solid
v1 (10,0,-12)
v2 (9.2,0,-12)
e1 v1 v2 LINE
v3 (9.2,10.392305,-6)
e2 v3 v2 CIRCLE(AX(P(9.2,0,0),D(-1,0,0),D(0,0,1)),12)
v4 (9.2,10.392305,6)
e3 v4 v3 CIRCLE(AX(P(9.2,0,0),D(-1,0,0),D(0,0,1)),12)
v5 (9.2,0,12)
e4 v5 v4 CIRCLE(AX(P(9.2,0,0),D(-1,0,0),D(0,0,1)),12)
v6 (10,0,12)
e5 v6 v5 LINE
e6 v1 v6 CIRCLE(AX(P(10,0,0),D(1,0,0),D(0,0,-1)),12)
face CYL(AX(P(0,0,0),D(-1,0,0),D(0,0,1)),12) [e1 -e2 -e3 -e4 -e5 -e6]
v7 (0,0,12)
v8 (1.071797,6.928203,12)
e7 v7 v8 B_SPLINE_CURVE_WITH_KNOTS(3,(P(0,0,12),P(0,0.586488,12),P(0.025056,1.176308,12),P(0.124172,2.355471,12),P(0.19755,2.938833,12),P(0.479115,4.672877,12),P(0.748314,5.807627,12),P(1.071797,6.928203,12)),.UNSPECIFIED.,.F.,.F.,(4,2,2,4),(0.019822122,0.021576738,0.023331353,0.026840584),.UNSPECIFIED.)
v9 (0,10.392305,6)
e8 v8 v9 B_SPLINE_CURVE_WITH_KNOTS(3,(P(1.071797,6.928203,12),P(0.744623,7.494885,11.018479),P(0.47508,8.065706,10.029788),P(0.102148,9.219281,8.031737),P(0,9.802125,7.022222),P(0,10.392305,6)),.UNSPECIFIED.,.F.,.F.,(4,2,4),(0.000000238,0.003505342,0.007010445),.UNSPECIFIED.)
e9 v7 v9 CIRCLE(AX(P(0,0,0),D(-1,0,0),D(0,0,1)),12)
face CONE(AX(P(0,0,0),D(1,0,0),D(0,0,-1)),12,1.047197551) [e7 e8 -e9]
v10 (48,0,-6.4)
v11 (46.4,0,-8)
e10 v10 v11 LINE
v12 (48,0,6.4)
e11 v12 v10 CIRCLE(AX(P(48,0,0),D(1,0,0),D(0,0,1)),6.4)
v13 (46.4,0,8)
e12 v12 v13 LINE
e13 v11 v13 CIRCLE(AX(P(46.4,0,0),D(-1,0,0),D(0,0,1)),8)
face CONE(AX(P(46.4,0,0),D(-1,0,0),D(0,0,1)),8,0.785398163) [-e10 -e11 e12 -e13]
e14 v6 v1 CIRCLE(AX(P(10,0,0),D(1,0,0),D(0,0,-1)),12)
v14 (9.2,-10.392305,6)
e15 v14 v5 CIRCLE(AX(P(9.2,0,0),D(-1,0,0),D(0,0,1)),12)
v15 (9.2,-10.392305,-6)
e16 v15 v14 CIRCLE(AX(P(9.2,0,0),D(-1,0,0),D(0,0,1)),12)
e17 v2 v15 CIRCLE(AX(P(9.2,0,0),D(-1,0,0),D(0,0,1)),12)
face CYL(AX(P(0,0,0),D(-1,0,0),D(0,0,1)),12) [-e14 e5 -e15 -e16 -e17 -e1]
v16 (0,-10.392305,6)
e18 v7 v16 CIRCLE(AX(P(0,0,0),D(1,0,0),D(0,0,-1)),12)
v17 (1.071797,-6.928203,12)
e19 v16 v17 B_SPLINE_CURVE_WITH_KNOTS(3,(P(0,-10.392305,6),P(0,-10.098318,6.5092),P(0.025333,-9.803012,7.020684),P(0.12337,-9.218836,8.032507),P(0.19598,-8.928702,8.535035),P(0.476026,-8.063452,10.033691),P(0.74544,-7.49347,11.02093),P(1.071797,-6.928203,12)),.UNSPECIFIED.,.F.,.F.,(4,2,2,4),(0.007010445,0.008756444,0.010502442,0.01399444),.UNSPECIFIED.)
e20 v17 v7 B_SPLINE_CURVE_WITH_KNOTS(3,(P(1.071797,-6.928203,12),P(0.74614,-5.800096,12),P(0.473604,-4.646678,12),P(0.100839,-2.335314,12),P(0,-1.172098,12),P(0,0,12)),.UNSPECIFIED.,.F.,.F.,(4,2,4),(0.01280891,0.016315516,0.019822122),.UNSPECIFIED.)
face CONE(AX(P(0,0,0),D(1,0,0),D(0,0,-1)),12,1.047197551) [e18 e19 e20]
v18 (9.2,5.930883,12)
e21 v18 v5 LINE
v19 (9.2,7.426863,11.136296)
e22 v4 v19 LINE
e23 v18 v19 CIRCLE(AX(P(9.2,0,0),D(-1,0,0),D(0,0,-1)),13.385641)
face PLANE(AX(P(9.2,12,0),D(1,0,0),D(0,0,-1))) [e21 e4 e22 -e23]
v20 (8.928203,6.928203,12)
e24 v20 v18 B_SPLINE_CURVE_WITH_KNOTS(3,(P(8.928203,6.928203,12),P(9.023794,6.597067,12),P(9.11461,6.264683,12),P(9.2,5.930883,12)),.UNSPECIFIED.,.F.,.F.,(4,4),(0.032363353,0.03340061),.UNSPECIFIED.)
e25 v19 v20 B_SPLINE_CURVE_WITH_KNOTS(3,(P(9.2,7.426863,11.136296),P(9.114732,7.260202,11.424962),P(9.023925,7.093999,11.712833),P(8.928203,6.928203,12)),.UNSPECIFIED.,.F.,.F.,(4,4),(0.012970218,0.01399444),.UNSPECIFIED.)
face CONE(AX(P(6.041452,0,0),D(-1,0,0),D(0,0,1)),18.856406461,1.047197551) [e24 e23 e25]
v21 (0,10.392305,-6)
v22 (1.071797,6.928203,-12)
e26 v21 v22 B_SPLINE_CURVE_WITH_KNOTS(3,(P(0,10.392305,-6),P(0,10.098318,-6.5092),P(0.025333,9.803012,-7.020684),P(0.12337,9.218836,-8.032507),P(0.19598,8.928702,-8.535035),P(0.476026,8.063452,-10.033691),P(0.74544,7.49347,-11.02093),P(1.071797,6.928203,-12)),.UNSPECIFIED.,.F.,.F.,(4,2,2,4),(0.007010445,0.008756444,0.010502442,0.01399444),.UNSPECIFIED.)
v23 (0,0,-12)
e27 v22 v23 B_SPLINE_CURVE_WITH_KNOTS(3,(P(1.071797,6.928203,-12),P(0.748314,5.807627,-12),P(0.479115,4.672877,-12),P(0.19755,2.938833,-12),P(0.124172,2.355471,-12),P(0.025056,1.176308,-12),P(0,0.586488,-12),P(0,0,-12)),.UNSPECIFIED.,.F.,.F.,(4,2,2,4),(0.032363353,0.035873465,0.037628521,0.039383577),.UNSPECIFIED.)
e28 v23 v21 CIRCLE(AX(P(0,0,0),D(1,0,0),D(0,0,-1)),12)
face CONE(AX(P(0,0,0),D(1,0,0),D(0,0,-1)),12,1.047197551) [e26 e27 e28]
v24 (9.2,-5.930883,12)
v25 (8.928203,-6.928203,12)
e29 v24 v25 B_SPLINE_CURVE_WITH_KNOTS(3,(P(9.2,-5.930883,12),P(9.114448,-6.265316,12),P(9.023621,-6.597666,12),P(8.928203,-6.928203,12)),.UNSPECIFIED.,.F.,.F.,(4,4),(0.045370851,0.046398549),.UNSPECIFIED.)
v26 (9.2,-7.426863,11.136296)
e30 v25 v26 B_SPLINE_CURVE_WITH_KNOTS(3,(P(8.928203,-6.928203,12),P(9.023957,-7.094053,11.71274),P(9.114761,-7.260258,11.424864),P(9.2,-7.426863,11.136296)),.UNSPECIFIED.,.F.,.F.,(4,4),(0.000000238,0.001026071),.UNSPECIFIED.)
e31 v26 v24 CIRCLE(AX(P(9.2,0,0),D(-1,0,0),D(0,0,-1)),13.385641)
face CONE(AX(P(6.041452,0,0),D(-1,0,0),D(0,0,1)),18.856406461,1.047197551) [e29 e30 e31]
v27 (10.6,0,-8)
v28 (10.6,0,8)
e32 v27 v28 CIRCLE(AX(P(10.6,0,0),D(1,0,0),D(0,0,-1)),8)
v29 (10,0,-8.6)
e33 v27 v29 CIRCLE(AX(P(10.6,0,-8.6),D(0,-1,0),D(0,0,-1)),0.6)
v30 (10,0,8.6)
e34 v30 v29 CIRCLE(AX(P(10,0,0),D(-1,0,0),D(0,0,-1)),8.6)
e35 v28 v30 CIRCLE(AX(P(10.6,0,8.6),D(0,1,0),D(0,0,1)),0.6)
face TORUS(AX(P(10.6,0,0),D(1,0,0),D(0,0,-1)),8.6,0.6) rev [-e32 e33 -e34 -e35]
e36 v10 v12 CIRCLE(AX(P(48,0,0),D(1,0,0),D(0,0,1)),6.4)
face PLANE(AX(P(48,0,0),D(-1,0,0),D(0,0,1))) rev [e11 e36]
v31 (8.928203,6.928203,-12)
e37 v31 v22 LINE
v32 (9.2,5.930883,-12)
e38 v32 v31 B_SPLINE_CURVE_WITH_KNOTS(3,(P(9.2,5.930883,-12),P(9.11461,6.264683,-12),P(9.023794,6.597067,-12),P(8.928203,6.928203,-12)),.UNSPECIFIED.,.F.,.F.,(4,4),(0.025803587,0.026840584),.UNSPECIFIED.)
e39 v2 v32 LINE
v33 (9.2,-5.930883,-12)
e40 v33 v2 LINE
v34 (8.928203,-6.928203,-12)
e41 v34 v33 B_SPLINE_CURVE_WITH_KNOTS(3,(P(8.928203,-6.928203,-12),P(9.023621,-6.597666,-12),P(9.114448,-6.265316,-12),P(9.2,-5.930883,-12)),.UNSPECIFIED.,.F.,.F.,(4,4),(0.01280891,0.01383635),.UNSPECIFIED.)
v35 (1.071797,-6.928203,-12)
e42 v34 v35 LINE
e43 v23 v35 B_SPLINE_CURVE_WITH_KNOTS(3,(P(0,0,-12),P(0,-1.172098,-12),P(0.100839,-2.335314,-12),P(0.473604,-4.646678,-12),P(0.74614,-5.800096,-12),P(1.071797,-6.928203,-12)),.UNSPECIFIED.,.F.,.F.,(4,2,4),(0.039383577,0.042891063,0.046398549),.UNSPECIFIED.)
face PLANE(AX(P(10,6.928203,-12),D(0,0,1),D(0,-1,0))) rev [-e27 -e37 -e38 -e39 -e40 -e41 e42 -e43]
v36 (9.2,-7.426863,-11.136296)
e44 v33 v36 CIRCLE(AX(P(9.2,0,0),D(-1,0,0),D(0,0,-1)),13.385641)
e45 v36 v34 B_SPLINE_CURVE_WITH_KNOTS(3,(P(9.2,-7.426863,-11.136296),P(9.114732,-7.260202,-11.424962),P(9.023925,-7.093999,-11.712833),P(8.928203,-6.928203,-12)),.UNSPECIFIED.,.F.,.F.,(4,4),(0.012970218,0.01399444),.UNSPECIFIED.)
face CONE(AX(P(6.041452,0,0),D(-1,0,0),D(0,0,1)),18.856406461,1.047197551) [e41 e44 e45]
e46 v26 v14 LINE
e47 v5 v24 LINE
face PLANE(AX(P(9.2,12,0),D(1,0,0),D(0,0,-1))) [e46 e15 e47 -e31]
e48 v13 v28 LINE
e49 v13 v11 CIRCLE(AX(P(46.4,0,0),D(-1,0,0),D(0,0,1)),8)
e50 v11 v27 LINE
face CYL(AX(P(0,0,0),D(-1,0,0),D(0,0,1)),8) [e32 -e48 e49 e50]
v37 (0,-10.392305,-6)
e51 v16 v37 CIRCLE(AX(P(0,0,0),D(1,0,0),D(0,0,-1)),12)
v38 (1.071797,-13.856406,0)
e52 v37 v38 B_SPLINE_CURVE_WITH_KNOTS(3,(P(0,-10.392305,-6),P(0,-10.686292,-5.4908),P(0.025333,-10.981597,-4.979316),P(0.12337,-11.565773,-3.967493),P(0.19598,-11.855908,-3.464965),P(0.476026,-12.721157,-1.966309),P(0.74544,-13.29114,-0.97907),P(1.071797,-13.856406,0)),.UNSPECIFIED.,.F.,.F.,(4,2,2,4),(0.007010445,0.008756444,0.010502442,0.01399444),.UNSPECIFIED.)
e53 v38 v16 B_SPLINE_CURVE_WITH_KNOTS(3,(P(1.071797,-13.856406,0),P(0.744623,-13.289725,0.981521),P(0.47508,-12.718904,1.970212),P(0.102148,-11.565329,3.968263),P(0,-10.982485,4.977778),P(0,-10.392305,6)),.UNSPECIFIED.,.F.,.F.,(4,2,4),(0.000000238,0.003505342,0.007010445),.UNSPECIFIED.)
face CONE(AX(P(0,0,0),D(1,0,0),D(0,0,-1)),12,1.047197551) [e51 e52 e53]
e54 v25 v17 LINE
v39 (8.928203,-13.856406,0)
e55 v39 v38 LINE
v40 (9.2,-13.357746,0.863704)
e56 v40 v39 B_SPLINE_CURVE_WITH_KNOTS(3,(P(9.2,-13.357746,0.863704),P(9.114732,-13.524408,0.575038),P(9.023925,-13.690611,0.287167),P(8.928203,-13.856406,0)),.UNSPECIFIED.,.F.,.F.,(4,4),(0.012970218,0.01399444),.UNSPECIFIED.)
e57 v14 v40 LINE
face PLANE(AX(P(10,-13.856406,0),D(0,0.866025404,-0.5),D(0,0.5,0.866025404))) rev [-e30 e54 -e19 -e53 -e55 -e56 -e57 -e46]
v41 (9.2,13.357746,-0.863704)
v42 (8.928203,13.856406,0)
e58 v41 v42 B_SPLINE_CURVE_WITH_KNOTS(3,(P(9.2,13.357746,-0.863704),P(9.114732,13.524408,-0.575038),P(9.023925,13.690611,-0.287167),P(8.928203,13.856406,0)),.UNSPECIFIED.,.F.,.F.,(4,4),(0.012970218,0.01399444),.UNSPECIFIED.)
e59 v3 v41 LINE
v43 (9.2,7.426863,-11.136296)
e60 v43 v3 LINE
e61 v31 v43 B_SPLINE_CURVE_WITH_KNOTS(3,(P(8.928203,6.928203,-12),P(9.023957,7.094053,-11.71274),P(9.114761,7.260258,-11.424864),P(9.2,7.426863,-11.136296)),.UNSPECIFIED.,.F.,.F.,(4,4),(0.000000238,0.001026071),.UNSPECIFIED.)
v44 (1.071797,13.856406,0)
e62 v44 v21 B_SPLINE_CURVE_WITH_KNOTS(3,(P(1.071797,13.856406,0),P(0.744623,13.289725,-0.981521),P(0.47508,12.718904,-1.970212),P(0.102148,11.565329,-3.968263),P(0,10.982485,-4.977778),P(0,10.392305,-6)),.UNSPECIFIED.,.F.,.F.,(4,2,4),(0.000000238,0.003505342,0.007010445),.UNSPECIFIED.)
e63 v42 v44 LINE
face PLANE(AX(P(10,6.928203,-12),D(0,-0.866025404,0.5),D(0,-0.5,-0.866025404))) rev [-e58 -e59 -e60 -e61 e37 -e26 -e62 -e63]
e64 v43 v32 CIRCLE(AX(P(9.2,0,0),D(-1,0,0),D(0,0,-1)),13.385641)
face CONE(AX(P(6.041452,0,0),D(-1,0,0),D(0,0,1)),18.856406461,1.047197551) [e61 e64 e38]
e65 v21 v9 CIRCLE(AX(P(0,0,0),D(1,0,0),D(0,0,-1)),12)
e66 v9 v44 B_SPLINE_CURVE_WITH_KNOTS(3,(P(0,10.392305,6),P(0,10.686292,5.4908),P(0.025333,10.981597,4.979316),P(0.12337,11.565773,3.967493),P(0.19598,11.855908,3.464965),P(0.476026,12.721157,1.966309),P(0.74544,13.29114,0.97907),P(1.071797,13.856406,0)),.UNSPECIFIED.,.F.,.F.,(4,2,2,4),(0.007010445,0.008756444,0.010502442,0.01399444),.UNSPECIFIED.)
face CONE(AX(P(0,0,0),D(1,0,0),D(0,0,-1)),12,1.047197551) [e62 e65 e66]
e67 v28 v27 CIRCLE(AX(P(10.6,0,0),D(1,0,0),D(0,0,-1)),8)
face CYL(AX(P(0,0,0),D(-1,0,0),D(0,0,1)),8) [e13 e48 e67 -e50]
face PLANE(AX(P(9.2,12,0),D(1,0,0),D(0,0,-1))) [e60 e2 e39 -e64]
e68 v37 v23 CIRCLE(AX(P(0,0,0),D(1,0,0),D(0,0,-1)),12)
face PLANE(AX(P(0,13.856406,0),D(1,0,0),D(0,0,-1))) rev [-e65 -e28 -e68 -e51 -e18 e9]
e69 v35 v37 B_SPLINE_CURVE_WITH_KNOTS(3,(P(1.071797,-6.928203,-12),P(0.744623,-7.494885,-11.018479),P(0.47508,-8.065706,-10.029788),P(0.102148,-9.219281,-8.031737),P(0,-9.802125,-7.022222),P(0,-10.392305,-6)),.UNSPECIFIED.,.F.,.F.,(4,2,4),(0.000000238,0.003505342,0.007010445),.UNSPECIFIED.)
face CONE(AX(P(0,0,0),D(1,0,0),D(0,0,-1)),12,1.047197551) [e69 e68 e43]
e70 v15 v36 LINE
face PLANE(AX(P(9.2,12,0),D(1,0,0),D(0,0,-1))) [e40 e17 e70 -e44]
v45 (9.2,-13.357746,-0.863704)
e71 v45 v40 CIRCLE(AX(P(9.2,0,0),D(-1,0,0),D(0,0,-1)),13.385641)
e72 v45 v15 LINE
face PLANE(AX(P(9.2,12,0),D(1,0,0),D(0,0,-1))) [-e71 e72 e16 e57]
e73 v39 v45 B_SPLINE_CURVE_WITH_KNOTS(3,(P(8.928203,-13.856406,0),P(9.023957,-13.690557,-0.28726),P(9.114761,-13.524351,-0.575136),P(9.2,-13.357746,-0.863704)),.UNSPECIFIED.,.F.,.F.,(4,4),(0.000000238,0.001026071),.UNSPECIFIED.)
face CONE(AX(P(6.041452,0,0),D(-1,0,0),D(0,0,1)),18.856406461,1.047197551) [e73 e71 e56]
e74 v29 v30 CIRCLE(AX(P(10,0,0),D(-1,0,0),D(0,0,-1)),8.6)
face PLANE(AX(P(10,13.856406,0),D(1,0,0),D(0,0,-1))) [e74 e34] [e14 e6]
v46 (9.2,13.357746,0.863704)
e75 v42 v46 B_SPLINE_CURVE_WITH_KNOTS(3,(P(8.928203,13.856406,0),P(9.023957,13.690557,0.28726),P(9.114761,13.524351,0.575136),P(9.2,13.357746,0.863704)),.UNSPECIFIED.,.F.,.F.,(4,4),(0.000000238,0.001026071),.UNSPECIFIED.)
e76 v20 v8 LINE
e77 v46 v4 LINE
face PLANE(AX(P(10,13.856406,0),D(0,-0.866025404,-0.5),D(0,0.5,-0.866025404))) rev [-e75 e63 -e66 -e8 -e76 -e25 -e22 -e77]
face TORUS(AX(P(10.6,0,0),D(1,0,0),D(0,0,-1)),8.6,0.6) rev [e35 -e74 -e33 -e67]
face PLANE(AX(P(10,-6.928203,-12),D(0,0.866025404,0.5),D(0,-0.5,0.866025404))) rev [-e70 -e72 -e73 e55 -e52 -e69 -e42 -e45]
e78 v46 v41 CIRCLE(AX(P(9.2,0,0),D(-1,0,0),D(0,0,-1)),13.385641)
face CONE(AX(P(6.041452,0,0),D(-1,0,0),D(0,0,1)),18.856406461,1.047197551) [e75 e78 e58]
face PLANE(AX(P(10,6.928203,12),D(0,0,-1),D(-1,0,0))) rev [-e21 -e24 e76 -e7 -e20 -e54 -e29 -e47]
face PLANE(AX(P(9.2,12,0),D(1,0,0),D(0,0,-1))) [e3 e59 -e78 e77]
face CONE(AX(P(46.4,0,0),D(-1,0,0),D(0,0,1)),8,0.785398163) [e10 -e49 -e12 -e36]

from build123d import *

# Parameters (mm, degrees)
BASE_EXTRUDE_DEPTH = 10
SKETCH4_W          = 0.8
SKETCH4_H          = 11.856406461
CHAMFER_2_SIZE     = 1.6
FILLET_2_R         = 0.6


with BuildPart() as part:
    # Sketch1 → Base-Extrude (new body)
    with BuildSketch(Plane(origin=(0, 0, 0), x_dir=(0, 0, -1), z_dir=(1, 0, 0))):
        Polygon((12, 6.92820323), (12, -6.92820323), (0, -13.856406461), (-12, -6.92820323), (-12, 6.92820323), (0, 13.856406461), align=None)
    extrude(amount=BASE_EXTRUDE_DEPTH)

    # Sketch2 → Boss-Revolve1 (revolve)
    with BuildSketch(Plane.XY, mode=Mode.PRIVATE) as boss_revolve1_sk:
        Polygon((0, 0), (48, 0), (48, 6.268), (48, 8), (27.8072, 8), (0, 8), align=None)
    revolve(boss_revolve1_sk.sketch.rotate(Axis((0, 0, 0), (1, 0, 0)), 90), axis=Axis((0, 0, 0), (1, 0, 0)))

    # Sketch3 → Cut-Revolve1 (revolve, cut)
    with BuildSketch(Plane.XY):
        Polygon((0, 12), (3.958548116, 18.856406461), (3.958548116, 23.856406461), (-10, 23.856406461), (-10, 12), align=None)
    revolve(axis=Axis((0, 0, 0), (1, 0, 0)), mode=Mode.SUBTRACT)

    # Sketch5 → Cut-Revolve2 (revolve, cut)
    with BuildSketch(Plane.XY):
        Polygon((10, 12), (6.041451884, 18.856406461), (6.041451884, 23.856406461), (16.041451884, 23.856406461), (16.041451884, 12), align=None)
    revolve(axis=Axis((0, 0, 0), (1, 0, 0)), mode=Mode.SUBTRACT)

    # Sketch4 → Cut-Revolve3 (revolve, cut)
    with BuildSketch(Plane.XY, mode=Mode.PRIVATE) as cut_revolve3_sk:
        with Locations((9.6, 17.928203231)):
            Rectangle(SKETCH4_W, SKETCH4_H)
    revolve(cut_revolve3_sk.sketch.rotate(Axis((0, 0, 0), (1, 0, 0)), 270), axis=Axis((0, 0, 0), (1, 0, 0)), mode=Mode.SUBTRACT)

    # Chamfer 2
    chamfer_2_edges = [part.edges().sort_by_distance(p)[0] for p in [
        (48, 0, -8),
    ]]
    chamfer(chamfer_2_edges, length=CHAMFER_2_SIZE)

    # Fillet 2
    fillet_2_edges = [part.edges().sort_by_distance(p)[0] for p in [
        (10, 0, -8),
    ]]
    fillet(fillet_2_edges, radius=FILLET_2_R)


solid = part.part
